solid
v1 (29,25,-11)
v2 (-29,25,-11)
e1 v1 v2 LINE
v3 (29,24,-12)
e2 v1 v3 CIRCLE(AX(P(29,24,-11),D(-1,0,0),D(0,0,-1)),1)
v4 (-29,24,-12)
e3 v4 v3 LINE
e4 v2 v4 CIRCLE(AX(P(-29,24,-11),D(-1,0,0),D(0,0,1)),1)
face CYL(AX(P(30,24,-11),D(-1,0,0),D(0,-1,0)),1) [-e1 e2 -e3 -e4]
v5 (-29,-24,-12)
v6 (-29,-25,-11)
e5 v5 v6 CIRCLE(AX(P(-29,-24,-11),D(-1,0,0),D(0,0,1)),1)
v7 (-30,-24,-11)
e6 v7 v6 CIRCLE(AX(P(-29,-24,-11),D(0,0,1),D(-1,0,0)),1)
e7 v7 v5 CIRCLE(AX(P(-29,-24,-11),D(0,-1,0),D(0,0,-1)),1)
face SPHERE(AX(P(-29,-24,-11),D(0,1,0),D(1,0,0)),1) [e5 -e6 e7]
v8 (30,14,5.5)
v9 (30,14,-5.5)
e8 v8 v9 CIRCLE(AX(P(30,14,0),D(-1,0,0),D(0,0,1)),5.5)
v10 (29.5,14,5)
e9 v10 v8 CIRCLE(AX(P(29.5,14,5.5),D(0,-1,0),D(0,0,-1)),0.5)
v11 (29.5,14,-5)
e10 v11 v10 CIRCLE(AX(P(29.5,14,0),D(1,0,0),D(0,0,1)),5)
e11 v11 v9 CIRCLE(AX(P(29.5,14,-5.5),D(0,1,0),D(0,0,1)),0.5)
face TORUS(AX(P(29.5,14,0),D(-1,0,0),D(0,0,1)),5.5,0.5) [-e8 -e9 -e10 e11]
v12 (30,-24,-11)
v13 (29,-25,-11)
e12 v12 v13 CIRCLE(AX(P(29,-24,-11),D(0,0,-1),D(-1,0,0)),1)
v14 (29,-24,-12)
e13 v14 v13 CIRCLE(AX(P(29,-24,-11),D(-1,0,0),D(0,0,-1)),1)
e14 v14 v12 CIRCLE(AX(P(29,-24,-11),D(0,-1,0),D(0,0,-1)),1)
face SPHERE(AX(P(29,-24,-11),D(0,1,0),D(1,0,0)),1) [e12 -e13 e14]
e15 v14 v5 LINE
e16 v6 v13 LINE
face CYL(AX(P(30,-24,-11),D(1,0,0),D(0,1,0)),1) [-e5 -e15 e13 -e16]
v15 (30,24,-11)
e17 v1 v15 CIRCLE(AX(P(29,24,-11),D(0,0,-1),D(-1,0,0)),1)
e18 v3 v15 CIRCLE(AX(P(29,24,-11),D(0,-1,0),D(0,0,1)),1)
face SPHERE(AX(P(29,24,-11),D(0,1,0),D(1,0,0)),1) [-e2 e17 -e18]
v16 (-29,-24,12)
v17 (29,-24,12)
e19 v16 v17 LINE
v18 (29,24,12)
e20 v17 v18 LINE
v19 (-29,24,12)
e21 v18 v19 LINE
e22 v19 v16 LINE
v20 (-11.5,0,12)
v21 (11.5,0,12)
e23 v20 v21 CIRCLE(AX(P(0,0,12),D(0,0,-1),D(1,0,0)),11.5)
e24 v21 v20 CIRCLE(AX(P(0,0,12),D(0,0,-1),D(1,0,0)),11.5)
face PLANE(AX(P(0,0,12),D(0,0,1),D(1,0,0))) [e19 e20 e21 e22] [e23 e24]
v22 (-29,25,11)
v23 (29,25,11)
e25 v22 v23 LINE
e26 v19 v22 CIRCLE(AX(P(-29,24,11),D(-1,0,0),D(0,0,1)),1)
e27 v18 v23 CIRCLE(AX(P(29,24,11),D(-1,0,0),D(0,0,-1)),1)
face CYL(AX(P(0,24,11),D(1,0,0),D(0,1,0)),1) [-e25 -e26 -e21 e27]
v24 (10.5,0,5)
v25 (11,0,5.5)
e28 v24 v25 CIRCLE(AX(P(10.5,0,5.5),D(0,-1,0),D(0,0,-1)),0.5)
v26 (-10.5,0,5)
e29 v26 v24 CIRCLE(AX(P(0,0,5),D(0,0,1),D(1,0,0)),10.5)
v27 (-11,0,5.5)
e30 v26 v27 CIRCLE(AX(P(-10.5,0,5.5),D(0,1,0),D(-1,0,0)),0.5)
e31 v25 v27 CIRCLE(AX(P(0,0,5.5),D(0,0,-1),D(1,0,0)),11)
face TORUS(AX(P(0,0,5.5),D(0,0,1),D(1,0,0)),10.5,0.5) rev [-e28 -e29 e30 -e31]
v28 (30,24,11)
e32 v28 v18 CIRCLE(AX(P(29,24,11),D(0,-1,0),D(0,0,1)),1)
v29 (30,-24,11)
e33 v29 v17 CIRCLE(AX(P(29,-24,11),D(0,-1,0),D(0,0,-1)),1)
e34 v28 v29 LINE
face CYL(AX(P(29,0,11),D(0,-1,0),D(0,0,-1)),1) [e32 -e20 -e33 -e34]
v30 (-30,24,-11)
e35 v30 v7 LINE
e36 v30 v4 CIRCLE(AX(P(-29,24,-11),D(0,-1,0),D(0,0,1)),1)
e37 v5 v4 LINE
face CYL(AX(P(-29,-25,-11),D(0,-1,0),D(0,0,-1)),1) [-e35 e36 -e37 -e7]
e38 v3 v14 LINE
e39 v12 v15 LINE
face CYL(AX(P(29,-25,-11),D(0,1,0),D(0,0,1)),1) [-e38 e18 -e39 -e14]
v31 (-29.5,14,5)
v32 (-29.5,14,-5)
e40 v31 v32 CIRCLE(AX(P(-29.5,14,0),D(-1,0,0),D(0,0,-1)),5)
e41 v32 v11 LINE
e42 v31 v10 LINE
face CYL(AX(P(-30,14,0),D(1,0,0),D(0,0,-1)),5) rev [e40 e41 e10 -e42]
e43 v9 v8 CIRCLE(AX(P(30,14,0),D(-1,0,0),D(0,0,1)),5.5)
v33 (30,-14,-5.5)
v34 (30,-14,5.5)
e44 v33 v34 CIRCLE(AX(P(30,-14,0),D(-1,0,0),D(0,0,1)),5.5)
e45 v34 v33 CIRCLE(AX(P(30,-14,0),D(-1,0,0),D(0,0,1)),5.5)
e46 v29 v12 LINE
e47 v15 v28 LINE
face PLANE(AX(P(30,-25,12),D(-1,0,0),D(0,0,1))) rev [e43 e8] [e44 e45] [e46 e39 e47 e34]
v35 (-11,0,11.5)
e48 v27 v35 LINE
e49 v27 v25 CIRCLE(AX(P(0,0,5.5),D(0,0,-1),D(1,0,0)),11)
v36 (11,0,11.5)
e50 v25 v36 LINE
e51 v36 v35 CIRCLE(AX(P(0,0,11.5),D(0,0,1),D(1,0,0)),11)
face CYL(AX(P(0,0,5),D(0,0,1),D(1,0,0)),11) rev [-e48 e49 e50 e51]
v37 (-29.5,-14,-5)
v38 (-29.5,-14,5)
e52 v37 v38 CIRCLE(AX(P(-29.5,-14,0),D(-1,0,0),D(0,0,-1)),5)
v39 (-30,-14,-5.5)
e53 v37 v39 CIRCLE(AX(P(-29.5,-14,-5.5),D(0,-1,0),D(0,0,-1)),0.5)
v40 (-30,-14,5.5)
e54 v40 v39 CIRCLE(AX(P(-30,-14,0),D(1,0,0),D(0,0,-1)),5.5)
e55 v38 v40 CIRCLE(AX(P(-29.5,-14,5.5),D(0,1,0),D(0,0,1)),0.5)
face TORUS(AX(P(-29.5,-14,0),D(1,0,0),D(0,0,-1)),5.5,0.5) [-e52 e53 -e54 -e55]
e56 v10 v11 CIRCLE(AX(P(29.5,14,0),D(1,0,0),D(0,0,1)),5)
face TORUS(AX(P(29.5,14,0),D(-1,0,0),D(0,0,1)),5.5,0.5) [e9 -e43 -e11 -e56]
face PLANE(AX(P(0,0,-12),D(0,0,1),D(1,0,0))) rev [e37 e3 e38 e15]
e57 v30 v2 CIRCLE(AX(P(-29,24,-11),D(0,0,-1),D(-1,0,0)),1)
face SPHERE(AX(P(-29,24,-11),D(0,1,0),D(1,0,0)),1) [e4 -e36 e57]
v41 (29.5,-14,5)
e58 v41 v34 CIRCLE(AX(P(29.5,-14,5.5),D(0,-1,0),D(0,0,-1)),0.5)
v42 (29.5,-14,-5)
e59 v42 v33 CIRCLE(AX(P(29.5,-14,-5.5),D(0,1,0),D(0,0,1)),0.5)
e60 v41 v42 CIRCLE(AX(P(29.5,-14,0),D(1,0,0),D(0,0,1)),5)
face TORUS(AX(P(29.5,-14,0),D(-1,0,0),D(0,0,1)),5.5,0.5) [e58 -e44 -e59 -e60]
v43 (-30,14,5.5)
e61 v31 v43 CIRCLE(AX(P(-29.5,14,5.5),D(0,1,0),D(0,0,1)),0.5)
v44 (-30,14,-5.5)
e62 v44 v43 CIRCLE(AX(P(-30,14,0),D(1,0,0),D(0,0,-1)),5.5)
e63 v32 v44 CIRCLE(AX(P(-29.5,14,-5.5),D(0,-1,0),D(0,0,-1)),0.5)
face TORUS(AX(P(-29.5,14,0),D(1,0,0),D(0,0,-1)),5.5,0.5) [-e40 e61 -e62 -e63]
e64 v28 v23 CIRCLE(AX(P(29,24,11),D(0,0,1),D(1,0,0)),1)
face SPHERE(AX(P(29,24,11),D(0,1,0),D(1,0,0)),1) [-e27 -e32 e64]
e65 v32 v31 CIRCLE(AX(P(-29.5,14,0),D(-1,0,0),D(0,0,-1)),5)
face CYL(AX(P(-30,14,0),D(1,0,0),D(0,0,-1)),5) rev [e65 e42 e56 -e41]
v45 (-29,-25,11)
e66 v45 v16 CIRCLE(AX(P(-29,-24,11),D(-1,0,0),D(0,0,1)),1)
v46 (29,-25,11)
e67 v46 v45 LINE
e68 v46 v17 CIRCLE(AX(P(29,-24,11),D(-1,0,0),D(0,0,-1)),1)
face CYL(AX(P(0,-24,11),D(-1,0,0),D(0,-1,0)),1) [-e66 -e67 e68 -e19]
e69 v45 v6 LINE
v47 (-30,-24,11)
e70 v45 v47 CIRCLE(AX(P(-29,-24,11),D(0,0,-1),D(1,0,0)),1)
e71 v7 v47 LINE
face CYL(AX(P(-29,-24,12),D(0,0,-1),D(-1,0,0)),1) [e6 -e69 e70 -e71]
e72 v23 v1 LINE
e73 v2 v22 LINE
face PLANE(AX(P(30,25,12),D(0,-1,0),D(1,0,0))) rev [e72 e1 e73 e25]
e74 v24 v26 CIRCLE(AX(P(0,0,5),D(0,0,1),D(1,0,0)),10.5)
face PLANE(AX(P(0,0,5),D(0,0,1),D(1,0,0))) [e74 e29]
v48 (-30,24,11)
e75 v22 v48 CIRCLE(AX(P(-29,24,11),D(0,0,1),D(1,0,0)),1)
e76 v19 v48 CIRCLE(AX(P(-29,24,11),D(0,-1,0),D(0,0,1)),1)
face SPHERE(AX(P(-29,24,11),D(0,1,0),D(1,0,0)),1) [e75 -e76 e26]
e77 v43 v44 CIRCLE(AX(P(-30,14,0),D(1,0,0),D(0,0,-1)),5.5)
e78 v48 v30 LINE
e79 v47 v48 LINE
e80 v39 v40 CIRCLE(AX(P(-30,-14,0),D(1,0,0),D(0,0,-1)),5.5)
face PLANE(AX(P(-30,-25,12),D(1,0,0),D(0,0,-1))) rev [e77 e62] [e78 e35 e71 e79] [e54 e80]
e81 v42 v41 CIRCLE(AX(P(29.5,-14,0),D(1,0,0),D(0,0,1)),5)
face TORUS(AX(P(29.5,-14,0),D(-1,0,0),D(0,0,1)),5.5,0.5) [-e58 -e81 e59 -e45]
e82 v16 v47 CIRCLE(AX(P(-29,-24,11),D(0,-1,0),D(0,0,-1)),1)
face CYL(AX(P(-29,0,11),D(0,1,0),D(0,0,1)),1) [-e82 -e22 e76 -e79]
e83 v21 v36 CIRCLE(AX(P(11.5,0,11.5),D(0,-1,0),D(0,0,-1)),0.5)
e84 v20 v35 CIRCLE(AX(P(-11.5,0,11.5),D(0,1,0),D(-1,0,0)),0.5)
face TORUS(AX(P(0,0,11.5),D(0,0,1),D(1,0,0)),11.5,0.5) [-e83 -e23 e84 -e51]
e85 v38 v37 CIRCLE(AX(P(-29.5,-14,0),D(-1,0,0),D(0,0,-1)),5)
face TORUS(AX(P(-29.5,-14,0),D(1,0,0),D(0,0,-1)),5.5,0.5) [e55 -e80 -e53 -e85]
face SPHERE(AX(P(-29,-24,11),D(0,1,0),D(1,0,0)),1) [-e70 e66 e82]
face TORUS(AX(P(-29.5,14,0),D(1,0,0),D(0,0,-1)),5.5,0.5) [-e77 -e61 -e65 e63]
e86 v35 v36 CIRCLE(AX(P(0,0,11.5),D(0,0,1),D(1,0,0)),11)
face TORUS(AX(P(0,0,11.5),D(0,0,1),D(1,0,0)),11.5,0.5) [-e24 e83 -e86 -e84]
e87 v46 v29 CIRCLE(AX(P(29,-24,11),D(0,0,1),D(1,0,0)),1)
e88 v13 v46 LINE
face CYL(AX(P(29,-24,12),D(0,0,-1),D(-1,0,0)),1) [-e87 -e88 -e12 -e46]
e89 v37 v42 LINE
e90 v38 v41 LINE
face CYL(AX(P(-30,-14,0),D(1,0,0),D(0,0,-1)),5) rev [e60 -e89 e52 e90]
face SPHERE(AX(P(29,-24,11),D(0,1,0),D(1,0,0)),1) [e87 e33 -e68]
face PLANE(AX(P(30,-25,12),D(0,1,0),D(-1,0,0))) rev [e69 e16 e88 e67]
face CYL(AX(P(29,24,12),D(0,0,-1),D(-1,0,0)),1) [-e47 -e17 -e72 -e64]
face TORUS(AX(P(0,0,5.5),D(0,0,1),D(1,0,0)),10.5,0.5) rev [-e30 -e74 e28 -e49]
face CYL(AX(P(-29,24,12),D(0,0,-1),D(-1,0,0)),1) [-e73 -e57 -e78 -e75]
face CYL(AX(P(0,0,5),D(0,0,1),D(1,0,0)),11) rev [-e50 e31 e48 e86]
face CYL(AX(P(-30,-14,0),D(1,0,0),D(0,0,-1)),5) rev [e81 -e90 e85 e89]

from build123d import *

# Parameters (mm, degrees)
SKETCH1_W           = 60
SKETCH1_H           = 50
BOSS_EXTRUDE1_DEPTH = 12
SKETCH2_R           = 11
CUT_EXTRUDE1_DEPTH  = 7
SKETCH3_R           = 5
CUT_EXTRUDE2_DEPTH  = 67.098411479
FILLET1_R           = 1
FILLET2_R           = 0.5


with BuildPart() as part:
    # Sketch1 → Boss-Extrude1 (new, symmetric)
    with BuildSketch(Plane.XY):
        Rectangle(SKETCH1_W, SKETCH1_H)
    extrude(amount=BOSS_EXTRUDE1_DEPTH, both=True)

    # Sketch2 → Cut-Extrude1 (cut)
    with BuildSketch(Plane.XY.offset(12)):
        Circle(SKETCH2_R)
    extrude(amount=-CUT_EXTRUDE1_DEPTH, mode=Mode.SUBTRACT)

    # Sketch3 → Cut-Extrude2 (cut, through all)
    with BuildSketch(Plane(origin=(30, 0, 0), x_dir=(0, 0, -1), z_dir=(1, 0, 0))):
        with Locations((0, 14)):
            Circle(SKETCH3_R)
        with Locations((0, -14)):
            Circle(SKETCH3_R)
    extrude(amount=-CUT_EXTRUDE2_DEPTH, mode=Mode.SUBTRACT)

    # Fillet1
    fillet1_edges = [part.edges().sort_by_distance(p)[0] for p in [
        (30, 0, 12),
        (0, 25, 12),
        (-30, 0, 12),
        (0, 25, -12),
        (30, 0, -12),
        (0, -25, -12),
        (-30, 0, -12),
        (0, -25, 12),
        (-30, 25, 0),
        (30, 25, 0),
        (30, -25, 0),
        (-30, -25, 0),
    ]]
    fillet(fillet1_edges, radius=FILLET1_R)

    # Fillet2
    fillet2_edges = [part.edges().sort_by_distance(p)[0] for p in [
        (-11, 0, 5),
        (-11, 0, 12),
        (-30, 14, 5),
        (30, 14, 5),
        (-30, -14, 5),
        (30, -14, 5),
    ]]
    fillet(fillet2_edges, radius=FILLET2_R)


solid = part.part
